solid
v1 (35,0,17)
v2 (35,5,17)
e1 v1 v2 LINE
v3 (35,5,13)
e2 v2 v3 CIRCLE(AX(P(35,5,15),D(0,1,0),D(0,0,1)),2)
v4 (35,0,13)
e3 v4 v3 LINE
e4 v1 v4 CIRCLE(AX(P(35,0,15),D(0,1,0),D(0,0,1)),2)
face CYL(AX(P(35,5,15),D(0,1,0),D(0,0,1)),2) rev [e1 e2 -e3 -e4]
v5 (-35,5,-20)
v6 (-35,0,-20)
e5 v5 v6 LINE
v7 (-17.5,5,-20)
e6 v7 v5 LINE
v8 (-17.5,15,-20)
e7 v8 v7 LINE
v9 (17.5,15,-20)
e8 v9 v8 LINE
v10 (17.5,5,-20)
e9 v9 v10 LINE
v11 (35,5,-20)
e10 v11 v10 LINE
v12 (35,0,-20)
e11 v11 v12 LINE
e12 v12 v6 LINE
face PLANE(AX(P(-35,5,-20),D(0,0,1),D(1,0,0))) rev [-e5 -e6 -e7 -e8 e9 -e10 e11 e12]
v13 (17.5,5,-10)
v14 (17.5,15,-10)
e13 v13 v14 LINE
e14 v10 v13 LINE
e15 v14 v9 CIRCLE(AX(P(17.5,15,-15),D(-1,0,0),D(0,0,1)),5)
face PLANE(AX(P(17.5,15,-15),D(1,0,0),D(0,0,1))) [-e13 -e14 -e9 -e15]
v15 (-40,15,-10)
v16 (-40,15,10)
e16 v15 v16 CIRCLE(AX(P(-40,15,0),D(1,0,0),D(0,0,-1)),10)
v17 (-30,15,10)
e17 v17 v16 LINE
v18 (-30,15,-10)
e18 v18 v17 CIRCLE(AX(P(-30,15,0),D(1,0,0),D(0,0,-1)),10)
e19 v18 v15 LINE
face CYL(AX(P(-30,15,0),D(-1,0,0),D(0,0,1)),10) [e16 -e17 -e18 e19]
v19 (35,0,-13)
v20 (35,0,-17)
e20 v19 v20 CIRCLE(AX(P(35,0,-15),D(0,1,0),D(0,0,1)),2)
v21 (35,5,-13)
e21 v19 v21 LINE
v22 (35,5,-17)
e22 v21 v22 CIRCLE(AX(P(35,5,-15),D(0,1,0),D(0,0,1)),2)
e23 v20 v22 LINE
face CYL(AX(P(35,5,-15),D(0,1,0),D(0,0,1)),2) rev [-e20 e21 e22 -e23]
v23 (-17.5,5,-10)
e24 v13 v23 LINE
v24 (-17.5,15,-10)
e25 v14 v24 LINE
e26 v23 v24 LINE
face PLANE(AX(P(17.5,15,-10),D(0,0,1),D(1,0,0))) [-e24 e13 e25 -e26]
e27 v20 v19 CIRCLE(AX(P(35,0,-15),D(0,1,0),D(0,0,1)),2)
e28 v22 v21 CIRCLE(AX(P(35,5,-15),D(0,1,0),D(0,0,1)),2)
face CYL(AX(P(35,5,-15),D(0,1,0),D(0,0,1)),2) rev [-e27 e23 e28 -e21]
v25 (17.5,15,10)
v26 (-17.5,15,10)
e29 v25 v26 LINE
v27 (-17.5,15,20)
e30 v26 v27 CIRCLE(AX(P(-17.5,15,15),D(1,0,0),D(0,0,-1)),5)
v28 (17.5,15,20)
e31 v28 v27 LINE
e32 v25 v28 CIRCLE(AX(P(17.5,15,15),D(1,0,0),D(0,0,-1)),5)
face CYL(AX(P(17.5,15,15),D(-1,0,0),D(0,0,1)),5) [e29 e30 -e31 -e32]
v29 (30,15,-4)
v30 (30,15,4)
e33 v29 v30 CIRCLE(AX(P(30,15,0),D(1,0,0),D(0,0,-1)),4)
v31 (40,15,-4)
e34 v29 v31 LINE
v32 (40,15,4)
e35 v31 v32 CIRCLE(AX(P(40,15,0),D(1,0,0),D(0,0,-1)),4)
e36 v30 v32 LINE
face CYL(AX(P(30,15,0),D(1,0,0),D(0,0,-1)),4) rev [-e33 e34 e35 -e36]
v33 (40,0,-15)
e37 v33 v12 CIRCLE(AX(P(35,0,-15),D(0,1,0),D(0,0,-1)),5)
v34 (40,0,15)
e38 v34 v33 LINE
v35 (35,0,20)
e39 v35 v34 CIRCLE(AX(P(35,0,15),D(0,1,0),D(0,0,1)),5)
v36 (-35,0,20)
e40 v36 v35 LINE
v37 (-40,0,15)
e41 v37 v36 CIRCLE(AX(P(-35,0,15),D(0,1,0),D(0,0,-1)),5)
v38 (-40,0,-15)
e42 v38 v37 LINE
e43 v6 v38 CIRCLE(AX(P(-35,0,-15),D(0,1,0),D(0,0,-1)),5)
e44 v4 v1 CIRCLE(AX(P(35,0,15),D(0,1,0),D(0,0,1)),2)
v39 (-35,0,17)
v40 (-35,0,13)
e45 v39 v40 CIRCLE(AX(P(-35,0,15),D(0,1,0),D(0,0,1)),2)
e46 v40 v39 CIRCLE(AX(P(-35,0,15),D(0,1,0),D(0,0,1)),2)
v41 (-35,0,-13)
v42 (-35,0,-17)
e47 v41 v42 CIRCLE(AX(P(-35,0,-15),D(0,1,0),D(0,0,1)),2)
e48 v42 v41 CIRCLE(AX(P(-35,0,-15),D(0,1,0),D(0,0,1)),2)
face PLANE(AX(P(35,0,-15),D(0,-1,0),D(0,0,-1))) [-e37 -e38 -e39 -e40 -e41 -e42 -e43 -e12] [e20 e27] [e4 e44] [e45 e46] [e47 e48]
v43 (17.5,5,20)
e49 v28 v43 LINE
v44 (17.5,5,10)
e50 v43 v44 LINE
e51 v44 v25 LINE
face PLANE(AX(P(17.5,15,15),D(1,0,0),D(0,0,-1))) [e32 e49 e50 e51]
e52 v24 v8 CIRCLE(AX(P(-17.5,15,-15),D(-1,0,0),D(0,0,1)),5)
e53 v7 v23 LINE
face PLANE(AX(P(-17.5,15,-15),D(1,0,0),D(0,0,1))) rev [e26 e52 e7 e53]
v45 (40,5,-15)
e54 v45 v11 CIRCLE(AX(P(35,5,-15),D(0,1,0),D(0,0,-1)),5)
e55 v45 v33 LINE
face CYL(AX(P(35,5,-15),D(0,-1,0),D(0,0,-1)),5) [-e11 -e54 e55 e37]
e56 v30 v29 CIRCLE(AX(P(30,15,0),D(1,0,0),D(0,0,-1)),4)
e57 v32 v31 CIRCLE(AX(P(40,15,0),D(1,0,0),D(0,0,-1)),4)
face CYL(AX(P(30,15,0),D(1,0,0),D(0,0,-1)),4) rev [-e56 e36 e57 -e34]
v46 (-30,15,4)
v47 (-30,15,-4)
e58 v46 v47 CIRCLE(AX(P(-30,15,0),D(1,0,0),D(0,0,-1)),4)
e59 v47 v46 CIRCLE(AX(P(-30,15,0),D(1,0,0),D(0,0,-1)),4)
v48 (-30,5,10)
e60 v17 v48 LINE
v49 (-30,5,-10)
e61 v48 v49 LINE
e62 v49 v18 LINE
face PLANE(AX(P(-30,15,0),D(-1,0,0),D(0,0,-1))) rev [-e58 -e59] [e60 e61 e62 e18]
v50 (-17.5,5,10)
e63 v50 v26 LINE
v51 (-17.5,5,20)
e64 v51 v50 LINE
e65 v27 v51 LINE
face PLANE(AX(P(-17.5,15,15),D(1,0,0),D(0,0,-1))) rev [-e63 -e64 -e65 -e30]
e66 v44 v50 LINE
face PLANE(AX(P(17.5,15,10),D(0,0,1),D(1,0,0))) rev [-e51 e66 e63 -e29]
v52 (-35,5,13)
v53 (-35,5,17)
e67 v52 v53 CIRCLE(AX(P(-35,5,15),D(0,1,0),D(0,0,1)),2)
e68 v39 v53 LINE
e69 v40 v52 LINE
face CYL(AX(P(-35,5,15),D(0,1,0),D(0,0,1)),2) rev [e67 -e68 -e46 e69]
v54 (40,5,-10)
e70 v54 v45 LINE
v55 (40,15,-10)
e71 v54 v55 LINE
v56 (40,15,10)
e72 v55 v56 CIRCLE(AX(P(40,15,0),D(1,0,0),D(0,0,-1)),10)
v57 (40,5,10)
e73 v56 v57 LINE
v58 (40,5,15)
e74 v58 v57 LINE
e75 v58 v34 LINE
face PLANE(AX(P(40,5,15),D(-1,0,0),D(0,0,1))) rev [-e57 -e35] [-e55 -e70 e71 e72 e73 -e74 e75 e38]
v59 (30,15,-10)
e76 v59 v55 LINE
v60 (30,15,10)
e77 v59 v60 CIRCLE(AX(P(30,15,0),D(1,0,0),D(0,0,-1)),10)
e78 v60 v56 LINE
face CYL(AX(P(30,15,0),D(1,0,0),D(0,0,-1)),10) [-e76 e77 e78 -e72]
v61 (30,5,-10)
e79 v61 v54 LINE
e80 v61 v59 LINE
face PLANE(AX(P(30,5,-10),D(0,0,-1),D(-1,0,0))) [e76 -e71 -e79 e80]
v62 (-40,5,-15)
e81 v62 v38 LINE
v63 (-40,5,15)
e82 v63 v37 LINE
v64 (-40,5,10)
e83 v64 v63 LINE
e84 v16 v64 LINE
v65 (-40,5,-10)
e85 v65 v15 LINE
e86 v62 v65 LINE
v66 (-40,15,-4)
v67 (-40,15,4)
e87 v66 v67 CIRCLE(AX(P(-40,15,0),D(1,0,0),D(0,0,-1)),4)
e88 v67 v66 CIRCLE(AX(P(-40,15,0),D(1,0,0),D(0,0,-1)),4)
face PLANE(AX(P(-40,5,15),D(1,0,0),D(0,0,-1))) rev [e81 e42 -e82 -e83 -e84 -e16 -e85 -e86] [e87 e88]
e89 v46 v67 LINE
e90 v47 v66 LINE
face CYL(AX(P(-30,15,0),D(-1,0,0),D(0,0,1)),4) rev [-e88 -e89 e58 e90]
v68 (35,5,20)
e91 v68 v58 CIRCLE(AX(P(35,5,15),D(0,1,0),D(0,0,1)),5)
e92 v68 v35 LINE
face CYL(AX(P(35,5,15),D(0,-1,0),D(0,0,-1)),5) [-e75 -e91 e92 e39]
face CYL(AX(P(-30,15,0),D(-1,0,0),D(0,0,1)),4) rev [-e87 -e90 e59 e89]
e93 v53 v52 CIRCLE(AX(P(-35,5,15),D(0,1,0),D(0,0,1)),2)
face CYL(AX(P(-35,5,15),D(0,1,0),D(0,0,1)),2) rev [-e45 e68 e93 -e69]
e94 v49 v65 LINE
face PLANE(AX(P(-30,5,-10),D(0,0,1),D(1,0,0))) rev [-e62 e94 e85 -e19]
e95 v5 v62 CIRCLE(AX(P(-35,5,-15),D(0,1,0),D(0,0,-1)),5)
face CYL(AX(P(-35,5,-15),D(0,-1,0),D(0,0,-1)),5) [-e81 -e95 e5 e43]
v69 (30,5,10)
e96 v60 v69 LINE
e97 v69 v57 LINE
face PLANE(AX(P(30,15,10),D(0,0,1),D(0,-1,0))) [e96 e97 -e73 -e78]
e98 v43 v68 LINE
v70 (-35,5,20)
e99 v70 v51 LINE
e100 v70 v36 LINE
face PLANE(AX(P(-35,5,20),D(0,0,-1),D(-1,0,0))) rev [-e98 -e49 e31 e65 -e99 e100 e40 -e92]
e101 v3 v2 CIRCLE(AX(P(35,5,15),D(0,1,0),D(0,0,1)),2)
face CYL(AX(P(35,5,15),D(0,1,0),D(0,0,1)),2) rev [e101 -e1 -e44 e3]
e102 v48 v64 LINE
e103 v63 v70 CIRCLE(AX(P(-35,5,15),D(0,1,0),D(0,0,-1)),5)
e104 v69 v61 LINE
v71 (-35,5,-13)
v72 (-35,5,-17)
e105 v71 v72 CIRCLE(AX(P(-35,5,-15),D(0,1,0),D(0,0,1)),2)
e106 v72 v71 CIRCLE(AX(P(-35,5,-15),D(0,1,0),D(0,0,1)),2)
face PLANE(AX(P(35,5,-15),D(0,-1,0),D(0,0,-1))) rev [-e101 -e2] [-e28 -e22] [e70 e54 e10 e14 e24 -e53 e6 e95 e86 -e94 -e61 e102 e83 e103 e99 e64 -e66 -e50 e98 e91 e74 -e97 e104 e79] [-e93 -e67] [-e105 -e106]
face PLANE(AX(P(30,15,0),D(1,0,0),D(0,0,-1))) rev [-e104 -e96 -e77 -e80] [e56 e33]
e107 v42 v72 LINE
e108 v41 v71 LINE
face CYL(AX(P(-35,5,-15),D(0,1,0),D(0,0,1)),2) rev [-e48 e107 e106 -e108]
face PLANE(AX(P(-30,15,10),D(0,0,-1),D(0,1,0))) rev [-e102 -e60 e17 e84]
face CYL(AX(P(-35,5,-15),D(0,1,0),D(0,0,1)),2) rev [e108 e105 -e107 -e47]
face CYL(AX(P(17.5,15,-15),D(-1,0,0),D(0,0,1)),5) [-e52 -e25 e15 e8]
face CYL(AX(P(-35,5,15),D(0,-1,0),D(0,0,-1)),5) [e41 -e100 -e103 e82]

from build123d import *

# Parameters (mm, degrees)
BASE_PLATE_DEPTH        = 5
MOUNTING_HOLES_4_THRU_D = 4
END_LUG_SKETCH_R        = 4
END_LUG_DEPTH           = 10
GUIDE_RAIL_DEPTH        = 17.5


with BuildPart() as part:
    # Base Plate Sketch → Base Plate (new body)
    with BuildSketch(Plane(origin=(0, 0, 0), x_dir=(1, 0, 0), z_dir=(0, 1, 0))):
        with BuildLine():
            Line((-35, -20), (35, -20))
            ThreePointArc((35, -20), (38.535533906, -18.535533906), (40, -15))
            Line((40, -15), (40, 15))
            ThreePointArc((40, 15), (38.535533906, 18.535533906), (35, 20))
            Line((35, 20), (-35, 20))
            ThreePointArc((-35, 20), (-38.535533906, 18.535533906), (-40, 15))
            Line((-40, 15), (-40, -15))
            ThreePointArc((-40, -15), (-38.535533906, -18.535533906), (-35, -20))
        make_face()
    extrude(amount=BASE_PLATE_DEPTH)

    # Mounting Holes Ø4 Thru (through all)
    with Locations(Plane(origin=(-35, 5, -15), x_dir=(0, 0, 1), z_dir=(0, 1, 0))):
        with Locations((0, 0), (0, 70), (30, 70), (30, 0)):
            Hole(MOUNTING_HOLES_4_THRU_D / 2)

    # End Lug Sketch → End Lug (add)
    with BuildSketch(Plane(origin=(40, 0, 0), x_dir=(0, 0, -1), z_dir=(1, 0, 0))):
        with BuildLine():
            Line((-10, 15), (-10, 5))
            Line((-10, 5), (10, 5))
            Line((10, 5), (10, 15))
            ThreePointArc((10, 15), (0, 25), (-10, 15))
        make_face()
        with Locations((0, 15)):
            Circle(END_LUG_SKETCH_R, mode=Mode.SUBTRACT)
    end_lug = extrude(amount=-END_LUG_DEPTH)

    # End Lug Mirror: End Lug across plane
    add(end_lug.mirror(Plane(origin=(0, 0, 0), x_dir=(0, 0, 1), z_dir=(1, 0, 0))))

    # Guide Rail Sketch → Guide Rail (add, symmetric)
    with BuildSketch(Plane(origin=(0, 0, 0), x_dir=(0, 0, -1), z_dir=(1, 0, 0))):
        with BuildLine():
            Line((-20, 5), (-20, 15))
            ThreePointArc((-20, 15), (-15, 20), (-10, 15))
            Line((-10, 15), (-10, 5))
            Line((-10, 5), (-20, 5))
        make_face()
    guide_rail = extrude(amount=GUIDE_RAIL_DEPTH, both=True)

    # Guide Rail Mirror: Guide Rail across plane
    add(guide_rail.mirror(Plane.XY))


solid = part.part
